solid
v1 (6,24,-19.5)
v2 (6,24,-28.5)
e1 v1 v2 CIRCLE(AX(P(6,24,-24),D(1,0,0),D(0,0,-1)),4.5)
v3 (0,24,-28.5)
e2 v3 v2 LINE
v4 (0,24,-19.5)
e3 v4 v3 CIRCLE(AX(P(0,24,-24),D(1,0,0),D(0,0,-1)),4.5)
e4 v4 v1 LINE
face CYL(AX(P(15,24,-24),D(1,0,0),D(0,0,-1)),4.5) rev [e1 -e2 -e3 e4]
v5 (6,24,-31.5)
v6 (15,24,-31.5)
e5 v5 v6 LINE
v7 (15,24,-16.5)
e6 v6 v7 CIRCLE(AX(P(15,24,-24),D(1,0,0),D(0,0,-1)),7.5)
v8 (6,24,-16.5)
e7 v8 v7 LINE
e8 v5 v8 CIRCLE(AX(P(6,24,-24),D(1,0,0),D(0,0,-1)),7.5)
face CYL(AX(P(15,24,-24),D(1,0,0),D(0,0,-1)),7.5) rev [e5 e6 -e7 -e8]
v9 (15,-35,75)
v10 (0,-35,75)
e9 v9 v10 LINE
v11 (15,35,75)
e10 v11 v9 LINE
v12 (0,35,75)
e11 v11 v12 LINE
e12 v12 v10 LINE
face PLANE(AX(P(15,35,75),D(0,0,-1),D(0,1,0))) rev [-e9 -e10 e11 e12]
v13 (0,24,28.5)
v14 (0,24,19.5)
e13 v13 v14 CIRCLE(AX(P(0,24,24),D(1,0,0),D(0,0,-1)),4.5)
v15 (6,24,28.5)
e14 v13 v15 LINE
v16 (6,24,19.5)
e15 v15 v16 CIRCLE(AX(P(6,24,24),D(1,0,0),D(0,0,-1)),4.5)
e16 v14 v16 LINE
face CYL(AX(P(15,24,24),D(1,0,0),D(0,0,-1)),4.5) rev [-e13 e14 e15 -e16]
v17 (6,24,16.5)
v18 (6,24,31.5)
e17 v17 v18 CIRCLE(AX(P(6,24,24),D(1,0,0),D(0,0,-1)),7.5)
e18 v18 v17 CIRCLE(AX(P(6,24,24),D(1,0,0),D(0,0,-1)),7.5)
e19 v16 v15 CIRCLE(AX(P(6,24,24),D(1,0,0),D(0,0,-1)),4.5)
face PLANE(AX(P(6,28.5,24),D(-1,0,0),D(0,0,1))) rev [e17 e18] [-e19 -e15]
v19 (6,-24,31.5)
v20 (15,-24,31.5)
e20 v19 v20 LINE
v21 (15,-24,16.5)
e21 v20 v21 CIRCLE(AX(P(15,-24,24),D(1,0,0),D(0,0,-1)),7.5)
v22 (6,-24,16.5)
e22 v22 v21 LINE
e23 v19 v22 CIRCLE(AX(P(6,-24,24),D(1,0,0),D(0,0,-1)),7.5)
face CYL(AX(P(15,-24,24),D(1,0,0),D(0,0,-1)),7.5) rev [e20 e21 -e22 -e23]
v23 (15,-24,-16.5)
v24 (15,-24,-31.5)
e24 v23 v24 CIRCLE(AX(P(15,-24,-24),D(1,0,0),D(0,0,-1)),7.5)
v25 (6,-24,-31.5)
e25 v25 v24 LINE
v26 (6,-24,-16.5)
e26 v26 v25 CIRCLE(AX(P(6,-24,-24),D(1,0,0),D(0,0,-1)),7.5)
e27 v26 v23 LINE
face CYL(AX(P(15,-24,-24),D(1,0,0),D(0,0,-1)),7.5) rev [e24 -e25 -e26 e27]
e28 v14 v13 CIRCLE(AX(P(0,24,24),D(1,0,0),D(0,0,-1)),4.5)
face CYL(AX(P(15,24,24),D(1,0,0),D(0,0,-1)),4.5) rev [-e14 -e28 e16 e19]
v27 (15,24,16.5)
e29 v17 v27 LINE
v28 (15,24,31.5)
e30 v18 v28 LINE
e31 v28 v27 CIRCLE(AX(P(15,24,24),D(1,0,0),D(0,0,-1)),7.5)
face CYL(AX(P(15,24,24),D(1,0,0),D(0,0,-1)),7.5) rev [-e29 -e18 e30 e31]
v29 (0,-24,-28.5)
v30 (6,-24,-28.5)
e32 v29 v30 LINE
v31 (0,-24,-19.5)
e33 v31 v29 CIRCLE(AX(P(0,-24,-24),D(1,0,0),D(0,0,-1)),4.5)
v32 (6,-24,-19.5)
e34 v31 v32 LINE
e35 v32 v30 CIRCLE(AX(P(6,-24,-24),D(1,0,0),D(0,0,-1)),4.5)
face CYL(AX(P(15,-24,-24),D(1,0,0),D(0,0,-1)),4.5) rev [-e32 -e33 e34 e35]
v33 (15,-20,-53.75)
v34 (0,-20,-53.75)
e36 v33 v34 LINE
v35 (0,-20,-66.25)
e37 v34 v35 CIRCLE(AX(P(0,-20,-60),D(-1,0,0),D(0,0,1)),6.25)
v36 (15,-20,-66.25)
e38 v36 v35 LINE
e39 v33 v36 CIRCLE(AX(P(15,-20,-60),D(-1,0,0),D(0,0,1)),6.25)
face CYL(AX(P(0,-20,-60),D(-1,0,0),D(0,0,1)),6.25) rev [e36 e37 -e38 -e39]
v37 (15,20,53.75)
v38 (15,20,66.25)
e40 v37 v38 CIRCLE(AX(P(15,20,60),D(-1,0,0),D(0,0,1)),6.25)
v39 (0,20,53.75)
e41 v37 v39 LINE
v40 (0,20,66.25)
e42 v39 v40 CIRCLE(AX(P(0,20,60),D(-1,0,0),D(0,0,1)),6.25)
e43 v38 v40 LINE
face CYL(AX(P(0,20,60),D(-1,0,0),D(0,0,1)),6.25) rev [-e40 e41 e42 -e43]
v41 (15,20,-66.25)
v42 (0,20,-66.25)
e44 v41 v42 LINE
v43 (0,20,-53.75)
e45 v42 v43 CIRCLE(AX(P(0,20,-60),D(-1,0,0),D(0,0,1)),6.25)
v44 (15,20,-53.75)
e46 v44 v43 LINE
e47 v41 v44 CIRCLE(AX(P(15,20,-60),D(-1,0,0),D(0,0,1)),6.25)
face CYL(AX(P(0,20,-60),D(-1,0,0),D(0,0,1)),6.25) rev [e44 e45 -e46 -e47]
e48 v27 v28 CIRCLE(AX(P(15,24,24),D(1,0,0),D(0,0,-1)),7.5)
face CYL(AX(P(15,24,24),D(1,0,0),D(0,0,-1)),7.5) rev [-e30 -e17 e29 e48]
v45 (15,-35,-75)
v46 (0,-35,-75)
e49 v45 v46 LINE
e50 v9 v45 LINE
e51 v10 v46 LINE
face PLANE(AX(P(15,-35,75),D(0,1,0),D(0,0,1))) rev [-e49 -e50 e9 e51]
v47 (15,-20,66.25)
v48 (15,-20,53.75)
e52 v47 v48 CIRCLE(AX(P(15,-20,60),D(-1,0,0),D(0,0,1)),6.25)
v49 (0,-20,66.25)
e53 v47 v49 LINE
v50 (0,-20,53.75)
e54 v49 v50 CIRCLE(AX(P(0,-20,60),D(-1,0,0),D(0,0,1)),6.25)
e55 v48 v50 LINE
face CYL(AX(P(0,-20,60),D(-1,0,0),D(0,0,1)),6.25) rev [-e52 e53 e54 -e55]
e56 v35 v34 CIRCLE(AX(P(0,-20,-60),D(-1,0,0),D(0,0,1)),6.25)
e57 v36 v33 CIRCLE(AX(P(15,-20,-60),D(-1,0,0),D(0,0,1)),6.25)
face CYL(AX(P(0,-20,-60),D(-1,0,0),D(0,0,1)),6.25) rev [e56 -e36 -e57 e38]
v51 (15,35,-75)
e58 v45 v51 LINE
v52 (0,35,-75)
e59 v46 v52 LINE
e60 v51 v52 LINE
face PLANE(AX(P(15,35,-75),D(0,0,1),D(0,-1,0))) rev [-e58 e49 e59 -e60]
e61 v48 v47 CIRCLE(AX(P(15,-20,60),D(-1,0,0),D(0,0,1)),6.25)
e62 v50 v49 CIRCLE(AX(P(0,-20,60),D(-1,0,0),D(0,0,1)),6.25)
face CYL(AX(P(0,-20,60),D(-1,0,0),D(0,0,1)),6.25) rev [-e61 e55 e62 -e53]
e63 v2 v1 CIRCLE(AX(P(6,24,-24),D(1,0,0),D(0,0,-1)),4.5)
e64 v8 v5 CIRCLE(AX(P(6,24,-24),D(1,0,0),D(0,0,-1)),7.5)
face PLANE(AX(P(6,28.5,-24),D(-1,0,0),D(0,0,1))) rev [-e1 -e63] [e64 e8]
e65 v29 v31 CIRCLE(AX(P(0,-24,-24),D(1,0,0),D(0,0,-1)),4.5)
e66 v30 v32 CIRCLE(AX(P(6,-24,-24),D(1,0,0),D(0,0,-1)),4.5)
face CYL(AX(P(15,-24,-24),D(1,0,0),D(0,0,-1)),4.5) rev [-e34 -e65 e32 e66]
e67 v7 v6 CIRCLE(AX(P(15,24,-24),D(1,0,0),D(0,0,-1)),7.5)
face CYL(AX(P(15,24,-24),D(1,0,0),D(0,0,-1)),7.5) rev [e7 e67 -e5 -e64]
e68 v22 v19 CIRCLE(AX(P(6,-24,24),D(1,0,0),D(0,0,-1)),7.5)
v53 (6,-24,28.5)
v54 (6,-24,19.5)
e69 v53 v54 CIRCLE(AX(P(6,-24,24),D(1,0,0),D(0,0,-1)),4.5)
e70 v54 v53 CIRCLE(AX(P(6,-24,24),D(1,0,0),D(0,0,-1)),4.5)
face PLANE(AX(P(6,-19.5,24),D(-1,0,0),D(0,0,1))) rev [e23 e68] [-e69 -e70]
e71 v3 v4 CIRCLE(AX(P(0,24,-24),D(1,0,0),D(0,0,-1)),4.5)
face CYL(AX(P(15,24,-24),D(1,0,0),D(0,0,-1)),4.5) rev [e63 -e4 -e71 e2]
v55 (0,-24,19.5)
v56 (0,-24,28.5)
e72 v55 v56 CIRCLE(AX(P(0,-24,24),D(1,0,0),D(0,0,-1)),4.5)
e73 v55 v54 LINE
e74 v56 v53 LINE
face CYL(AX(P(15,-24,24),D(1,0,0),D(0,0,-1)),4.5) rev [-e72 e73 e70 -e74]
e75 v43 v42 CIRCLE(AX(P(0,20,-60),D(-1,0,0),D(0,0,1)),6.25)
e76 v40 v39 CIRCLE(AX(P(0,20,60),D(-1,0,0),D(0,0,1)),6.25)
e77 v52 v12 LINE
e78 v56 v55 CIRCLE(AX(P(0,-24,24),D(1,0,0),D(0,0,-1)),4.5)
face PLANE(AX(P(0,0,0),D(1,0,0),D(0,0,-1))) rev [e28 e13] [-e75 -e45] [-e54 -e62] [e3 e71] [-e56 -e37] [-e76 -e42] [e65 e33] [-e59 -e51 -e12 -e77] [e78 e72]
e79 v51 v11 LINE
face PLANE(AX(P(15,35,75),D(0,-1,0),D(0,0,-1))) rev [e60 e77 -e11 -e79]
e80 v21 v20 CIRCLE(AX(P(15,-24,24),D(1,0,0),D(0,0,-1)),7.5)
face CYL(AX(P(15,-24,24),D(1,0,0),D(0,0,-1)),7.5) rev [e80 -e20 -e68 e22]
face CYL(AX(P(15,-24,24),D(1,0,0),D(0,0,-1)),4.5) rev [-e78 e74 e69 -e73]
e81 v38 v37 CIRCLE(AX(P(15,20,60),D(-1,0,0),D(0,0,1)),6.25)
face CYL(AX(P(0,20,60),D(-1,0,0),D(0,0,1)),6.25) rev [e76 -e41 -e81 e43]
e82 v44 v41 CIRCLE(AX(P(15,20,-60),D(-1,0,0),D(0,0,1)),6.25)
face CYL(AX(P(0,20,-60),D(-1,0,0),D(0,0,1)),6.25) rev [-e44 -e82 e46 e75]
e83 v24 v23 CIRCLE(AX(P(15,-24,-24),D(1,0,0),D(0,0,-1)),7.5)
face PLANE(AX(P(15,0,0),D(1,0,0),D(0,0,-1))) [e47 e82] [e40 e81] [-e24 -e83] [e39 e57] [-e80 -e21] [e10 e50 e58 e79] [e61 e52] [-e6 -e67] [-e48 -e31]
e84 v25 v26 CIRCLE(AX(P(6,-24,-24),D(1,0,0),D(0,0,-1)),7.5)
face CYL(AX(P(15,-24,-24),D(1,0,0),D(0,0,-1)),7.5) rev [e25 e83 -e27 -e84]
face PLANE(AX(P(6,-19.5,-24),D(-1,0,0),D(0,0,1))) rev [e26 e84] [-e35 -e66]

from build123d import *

# Parameters (mm, degrees)
SKETCH_1_W                = 150
SKETCH_1_H                = 70
EXTRUDE_1_DEPTH           = 15
HOLE_WIZARD_1_D           = 9
HOLE_WIZARD_1_CBORE_D     = 15
HOLE_WIZARD_1_CBORE_DEPTH = 9
HOLE_WIZARD_12_5_12_5_1_D = 12.5


with BuildPart() as part:
    # 草图1 → 凸台-拉伸1 (new body)
    with BuildSketch(Plane(origin=(0, 0, 0), x_dir=(0, 0, -1), z_dir=(1, 0, 0))):
        Rectangle(SKETCH_1_W, SKETCH_1_H)
    extrude(amount=EXTRUDE_1_DEPTH)

    # 打孔尺寸(%根据)内六角圆柱头螺钉的类型1 (through all)
    with Locations(Plane(origin=(15, 0, 0), x_dir=(0, 0, -1), z_dir=(1, 0, 0))):
        with Locations((-24, 24), (24, 24), (-24, -24), (24, -24)):
            CounterBoreHole(HOLE_WIZARD_1_D / 2, HOLE_WIZARD_1_CBORE_D / 2, HOLE_WIZARD_1_CBORE_DEPTH)

    # Ø12.5 (12.5) 直径孔1 (through all)
    with Locations(Plane.ZY):
        with Locations((-60, 20), (-60, -20), (60, 20), (60, -20)):
            Hole(HOLE_WIZARD_12_5_12_5_1_D / 2)


solid = part.part
